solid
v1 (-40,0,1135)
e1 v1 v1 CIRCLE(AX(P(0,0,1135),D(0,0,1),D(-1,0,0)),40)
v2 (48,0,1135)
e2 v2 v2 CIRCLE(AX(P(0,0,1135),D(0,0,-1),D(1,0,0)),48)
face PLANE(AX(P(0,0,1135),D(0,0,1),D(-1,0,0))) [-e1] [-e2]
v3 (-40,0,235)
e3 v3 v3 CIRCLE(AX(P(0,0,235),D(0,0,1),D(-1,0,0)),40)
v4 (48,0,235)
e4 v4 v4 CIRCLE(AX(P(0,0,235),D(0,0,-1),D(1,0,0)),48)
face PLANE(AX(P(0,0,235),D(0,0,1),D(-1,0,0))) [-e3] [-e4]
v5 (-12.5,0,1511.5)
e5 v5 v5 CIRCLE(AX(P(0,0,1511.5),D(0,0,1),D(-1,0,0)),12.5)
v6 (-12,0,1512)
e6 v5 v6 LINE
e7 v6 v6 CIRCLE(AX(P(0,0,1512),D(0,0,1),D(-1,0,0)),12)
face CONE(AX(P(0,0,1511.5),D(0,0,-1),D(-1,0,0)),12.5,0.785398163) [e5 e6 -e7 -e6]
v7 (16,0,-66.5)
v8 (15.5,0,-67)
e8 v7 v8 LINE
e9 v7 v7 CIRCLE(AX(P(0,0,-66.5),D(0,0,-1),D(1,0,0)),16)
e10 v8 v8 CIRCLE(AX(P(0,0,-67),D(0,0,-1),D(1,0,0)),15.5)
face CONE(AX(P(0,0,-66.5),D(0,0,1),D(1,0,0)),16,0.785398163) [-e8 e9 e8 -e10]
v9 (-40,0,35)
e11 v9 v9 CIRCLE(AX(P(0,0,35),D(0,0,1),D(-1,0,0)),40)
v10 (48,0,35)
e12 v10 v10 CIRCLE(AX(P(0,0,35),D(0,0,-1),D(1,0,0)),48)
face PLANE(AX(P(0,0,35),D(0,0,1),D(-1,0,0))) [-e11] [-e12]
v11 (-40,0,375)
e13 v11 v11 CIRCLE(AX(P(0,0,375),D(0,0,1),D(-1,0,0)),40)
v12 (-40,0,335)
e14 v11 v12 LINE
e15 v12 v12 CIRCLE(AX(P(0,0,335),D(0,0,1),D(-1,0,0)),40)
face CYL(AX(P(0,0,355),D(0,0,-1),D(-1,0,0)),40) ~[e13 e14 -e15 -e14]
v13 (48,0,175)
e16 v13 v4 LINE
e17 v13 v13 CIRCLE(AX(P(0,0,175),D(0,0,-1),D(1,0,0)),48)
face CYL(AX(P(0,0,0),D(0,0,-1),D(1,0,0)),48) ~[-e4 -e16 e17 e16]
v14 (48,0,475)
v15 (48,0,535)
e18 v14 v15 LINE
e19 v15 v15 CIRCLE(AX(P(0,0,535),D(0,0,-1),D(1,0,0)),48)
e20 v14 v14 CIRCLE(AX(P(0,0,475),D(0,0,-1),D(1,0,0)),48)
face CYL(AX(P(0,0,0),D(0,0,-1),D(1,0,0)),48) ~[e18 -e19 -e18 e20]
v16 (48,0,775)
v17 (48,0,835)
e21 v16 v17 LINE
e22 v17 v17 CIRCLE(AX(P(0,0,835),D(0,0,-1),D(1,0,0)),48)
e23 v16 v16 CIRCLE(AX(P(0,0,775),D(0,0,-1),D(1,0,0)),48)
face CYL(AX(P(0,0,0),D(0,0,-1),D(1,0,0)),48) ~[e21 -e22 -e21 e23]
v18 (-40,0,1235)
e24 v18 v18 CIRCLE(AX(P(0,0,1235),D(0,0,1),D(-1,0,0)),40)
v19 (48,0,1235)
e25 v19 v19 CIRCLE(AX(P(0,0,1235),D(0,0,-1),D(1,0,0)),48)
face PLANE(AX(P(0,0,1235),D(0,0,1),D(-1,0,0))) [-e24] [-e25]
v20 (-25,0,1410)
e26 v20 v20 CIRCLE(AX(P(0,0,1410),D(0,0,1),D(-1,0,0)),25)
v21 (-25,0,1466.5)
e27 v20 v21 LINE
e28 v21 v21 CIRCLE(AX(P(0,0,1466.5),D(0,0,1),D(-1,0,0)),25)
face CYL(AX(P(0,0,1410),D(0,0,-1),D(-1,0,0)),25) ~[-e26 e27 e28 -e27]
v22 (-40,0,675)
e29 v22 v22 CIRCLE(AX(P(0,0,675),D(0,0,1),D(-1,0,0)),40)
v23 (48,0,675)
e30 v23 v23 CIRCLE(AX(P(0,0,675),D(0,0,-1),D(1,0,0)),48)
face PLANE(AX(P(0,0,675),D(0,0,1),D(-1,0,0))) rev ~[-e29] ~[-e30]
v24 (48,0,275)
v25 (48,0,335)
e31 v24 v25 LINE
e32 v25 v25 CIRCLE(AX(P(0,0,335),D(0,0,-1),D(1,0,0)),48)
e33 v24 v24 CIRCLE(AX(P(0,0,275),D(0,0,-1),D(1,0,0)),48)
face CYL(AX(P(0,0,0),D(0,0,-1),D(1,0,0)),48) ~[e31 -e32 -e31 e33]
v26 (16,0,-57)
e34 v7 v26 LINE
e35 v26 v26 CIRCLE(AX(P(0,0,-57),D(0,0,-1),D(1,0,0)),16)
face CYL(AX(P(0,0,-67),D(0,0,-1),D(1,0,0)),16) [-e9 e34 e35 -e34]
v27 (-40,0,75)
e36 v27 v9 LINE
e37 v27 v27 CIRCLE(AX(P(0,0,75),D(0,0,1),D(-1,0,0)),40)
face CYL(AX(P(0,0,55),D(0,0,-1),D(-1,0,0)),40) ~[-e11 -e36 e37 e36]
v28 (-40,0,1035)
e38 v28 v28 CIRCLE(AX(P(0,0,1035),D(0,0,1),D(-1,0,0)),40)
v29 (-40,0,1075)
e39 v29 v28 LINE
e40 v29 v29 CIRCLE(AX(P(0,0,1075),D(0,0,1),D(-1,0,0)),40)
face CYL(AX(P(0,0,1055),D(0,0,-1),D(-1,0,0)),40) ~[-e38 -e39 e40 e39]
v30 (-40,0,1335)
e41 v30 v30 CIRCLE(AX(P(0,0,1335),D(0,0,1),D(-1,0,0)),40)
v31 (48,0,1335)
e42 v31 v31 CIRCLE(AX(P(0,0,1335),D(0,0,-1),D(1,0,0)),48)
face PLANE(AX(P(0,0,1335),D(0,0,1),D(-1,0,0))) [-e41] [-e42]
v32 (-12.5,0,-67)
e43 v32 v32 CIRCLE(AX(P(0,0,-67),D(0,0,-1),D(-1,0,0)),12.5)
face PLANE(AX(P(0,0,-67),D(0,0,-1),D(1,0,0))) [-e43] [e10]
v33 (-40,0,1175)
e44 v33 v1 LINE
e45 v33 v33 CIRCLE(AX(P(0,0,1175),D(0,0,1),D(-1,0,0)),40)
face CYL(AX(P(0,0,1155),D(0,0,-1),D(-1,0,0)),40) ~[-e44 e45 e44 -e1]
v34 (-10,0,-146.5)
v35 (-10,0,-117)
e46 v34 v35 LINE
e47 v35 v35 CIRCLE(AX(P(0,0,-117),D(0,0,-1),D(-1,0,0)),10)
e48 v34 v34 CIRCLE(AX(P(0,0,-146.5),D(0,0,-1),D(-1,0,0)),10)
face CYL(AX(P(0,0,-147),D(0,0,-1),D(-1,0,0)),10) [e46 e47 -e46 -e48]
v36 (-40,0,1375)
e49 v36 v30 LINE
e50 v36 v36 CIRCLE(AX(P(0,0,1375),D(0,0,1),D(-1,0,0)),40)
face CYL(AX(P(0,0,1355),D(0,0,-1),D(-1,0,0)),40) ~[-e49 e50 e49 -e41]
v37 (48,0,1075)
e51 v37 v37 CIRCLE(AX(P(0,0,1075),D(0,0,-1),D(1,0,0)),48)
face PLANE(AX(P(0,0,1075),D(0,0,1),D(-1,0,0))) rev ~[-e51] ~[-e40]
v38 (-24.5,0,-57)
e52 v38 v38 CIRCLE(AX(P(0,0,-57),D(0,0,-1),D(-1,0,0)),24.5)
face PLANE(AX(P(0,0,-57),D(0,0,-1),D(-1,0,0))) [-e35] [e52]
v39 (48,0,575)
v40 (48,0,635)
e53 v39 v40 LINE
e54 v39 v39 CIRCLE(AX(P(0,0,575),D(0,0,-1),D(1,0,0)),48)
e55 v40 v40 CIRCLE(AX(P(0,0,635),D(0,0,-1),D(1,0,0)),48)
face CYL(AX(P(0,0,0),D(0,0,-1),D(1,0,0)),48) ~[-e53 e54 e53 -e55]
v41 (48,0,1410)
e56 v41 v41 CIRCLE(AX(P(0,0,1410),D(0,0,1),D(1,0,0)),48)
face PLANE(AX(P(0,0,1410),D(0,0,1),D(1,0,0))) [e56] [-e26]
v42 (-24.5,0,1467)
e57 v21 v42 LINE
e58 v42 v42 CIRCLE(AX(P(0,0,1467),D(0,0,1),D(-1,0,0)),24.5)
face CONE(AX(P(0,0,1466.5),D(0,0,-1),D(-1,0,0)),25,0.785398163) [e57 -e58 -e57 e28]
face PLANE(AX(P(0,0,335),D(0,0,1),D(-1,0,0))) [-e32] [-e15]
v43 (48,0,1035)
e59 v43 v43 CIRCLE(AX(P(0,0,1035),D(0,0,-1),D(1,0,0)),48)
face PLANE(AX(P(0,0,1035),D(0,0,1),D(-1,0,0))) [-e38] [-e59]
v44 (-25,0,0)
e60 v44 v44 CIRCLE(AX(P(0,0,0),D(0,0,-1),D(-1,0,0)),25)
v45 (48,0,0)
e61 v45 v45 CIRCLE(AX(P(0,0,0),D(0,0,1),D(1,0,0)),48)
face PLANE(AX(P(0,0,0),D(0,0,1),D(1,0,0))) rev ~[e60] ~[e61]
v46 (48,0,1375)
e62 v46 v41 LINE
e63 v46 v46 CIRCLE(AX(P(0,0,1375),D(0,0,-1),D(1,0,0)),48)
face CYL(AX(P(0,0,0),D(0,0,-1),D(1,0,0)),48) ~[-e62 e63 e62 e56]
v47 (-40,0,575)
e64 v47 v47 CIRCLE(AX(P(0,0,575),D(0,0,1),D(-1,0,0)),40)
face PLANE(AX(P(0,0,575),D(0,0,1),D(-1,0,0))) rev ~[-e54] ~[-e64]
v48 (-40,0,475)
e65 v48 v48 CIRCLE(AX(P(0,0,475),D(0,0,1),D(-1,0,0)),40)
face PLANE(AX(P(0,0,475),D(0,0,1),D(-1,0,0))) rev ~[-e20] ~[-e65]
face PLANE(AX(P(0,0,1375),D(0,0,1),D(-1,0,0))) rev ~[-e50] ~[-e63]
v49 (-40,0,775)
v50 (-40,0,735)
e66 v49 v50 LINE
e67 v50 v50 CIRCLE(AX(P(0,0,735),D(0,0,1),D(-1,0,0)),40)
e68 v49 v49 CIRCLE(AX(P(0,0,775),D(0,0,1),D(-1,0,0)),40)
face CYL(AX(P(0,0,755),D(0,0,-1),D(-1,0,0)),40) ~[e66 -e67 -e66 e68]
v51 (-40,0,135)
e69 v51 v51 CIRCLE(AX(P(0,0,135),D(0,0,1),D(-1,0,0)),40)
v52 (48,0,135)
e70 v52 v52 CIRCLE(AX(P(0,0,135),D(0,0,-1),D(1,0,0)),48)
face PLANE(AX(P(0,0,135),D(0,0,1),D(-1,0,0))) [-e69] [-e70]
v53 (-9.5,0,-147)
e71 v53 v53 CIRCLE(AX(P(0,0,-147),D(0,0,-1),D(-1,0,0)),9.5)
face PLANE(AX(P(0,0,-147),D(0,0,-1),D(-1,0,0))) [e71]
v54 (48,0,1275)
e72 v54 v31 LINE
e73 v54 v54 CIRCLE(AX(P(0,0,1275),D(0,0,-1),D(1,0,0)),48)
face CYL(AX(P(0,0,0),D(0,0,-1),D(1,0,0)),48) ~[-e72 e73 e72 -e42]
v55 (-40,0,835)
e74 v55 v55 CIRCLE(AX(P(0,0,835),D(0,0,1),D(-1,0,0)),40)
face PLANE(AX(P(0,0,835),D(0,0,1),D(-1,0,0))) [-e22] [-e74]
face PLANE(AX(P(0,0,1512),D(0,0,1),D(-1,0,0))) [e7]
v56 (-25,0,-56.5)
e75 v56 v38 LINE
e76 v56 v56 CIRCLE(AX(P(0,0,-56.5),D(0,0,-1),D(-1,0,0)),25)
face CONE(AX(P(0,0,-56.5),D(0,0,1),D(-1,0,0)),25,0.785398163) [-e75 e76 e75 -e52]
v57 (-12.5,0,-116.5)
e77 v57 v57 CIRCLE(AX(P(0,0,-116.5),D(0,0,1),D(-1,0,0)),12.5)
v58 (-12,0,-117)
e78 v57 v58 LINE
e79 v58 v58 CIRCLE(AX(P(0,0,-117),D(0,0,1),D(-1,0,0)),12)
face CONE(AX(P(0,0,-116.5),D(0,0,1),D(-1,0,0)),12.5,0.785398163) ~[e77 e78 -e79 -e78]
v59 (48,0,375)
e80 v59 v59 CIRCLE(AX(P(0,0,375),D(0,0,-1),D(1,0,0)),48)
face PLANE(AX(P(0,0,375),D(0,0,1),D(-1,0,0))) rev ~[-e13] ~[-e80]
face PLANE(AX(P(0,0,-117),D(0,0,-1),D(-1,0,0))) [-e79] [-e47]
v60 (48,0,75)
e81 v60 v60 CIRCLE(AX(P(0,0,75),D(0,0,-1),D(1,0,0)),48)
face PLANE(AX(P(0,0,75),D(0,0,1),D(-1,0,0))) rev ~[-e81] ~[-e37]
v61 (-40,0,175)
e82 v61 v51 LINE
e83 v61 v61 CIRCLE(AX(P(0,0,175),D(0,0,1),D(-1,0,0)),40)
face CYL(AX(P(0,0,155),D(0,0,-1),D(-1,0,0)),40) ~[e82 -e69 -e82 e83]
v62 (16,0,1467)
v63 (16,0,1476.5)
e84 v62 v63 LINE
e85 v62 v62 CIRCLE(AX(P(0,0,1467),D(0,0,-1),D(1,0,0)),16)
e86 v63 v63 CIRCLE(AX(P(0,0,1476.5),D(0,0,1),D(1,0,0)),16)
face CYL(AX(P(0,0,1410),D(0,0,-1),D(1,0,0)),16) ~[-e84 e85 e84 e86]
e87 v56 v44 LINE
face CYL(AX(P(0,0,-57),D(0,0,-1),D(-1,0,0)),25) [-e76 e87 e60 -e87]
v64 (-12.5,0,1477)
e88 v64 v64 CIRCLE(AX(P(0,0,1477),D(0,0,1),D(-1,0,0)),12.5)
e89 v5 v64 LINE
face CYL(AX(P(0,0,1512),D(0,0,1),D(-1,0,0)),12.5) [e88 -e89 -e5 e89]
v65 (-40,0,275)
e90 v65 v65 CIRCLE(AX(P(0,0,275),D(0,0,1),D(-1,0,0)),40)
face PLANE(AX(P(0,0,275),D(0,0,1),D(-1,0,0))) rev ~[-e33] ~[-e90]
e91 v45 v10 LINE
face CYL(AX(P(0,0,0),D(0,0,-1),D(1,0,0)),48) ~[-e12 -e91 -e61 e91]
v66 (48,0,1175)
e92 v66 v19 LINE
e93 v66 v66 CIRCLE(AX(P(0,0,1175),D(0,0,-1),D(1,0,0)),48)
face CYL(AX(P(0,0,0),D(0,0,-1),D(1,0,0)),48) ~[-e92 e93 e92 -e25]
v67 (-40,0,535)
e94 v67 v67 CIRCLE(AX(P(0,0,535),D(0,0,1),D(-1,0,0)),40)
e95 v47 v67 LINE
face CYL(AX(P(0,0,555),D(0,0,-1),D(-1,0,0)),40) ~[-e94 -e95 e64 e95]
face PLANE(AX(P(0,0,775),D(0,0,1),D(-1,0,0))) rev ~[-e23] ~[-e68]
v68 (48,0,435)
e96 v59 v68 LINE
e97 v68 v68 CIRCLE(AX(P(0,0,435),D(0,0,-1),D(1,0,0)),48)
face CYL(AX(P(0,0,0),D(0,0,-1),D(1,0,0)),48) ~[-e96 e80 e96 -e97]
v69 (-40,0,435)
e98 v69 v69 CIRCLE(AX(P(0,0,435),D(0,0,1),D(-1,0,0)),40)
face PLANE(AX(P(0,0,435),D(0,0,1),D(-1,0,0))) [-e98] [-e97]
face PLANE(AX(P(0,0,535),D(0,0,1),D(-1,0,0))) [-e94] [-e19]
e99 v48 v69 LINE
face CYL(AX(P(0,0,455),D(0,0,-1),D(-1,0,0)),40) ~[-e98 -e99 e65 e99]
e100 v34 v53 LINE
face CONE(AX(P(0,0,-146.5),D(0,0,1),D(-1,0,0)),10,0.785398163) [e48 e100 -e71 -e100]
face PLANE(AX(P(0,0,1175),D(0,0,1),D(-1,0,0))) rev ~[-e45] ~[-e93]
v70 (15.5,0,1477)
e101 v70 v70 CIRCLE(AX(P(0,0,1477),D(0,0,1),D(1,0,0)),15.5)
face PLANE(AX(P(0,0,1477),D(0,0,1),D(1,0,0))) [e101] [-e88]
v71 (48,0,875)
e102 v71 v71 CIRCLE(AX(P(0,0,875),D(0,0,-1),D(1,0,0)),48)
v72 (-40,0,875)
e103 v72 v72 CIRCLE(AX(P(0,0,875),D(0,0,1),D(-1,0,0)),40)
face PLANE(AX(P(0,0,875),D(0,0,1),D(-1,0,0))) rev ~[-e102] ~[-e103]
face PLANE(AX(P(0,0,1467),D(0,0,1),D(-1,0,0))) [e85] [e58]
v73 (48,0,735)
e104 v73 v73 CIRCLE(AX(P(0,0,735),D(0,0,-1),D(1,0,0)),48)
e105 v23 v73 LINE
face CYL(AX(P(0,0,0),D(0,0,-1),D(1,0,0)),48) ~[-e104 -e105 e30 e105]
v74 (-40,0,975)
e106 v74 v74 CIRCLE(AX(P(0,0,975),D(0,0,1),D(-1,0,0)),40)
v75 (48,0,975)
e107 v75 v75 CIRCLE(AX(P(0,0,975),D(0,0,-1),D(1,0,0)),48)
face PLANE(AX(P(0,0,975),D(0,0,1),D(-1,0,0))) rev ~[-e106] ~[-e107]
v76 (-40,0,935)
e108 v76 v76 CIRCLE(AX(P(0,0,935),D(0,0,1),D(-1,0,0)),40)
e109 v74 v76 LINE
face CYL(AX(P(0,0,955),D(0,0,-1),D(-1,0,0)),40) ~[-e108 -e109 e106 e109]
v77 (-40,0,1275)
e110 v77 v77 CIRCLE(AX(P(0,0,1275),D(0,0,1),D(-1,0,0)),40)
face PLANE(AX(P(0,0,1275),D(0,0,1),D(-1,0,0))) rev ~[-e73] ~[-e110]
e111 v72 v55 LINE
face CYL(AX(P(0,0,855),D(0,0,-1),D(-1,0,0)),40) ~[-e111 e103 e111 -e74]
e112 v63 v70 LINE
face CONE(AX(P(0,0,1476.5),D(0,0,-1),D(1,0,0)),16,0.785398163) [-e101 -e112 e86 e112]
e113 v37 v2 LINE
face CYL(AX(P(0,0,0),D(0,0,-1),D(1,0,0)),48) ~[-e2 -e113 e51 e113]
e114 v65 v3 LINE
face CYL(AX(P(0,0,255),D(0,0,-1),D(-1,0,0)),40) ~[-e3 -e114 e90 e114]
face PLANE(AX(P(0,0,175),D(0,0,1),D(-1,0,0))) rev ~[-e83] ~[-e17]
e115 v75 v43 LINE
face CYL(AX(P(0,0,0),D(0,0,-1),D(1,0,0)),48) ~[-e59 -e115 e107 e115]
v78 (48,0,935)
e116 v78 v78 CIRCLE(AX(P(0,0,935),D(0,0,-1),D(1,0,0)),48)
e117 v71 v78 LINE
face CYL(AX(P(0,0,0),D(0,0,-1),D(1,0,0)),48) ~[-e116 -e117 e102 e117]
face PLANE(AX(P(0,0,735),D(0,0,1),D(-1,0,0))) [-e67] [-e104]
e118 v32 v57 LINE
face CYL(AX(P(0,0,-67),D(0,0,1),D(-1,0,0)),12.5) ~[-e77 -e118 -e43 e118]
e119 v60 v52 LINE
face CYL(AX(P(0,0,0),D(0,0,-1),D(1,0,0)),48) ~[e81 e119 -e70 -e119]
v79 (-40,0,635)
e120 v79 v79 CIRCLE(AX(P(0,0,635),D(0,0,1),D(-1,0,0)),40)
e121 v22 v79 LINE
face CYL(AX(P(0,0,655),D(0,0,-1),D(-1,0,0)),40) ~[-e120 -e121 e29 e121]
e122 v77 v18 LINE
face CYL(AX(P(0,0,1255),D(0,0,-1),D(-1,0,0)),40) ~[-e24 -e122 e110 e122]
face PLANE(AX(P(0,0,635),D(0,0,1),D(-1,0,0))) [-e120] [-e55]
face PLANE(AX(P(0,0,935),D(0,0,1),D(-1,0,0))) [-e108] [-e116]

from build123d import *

# Parameters (mm, degrees)
SKETCH_1_R             = 48
EXTRUDE_1_DEPTH        = 1410
SKETCH_2_R             = 16
EXTRUDE_2_DEPTH        = 67
EXTRUDE_START          = 67
SKETCH_3_R             = 16
EXTRUDE_3_DEPTH        = 67
SKETCH_4_R             = 12.5
EXTRUDE_4_DEPTH        = 80
EXTRUDE_START_2        = 35
SKETCH_5_R             = 12.5
EXTRUDE_5_DEPTH        = 35
SKETCH_6_OUTSIDE_W     = 430.91
SKETCH_6_OUTSIDE_H     = 430.91
SKETCH_6_OUTSIDE_R     = 10
CUT_EXTRUDE_1_DEPTH    = 30
SKETCH_7_W             = 40
SKETCH_7_H             = 8
PATTERN_LINEAR_1_COUNT = 14
PATTERN_LINEAR_1_PITCH = 100
SKETCH_9_R             = 25
EXTRUDE_6_DEPTH        = 57
EXTRUDE_START_3        = 57
SKETCH_10_R            = 25
EXTRUDE_7_DEPTH        = 57
CHAMFER_1_SIZE         = 0.5


with BuildPart() as part:
    # 草图1 → 凸台-拉伸1 (new body)
    with BuildSketch(Plane.XY):
        Circle(SKETCH_1_R)
    extrude(amount=EXTRUDE_1_DEPTH)

    # 草图2 → 凸台-拉伸2 (add)
    with BuildSketch(Plane.XY.offset(1410)):
        Circle(SKETCH_2_R)
    extrude(amount=EXTRUDE_2_DEPTH)

    # 草图3 → 凸台-拉伸3 (add)
    with BuildSketch(Plane(origin=(0, 0, 0), x_dir=(-1, 0, 0), z_dir=(0, 0, -1)).offset(EXTRUDE_START)):
        with Locations(Location((0, 0, 0), (0, 0, 180))):
            Circle(SKETCH_3_R)
    extrude(amount=-EXTRUDE_3_DEPTH)

    # 草图4 → 凸台-拉伸4 (add)
    with BuildSketch(Plane(origin=(0, 0, -67), x_dir=(-1, 0, 0), z_dir=(0, 0, -1))):
        Circle(SKETCH_4_R)
    extrude(amount=EXTRUDE_4_DEPTH)

    # 草图5 → 凸台-拉伸5 (add)
    with BuildSketch(Plane.XY.offset(1477).offset(EXTRUDE_START_2)):
        with Locations(Location((0, 0, 0), (0, 0, 180))):
            Circle(SKETCH_5_R)
    extrude(amount=-EXTRUDE_5_DEPTH)

    # 草图6 outside → 切除-拉伸1 (cut)
    with BuildSketch(Plane(origin=(0, 0, -147), x_dir=(-1, 0, 0), z_dir=(0, 0, -1))):
        Rectangle(SKETCH_6_OUTSIDE_W, SKETCH_6_OUTSIDE_H)
        Circle(SKETCH_6_OUTSIDE_R, mode=Mode.SUBTRACT)
    extrude(amount=-CUT_EXTRUDE_1_DEPTH, mode=Mode.SUBTRACT)

    # 草图7 → 切除-旋转1 (revolve, cut)
    with BuildSketch(Plane(origin=(0, 0, 0), x_dir=(0, 0, -1), z_dir=(1, 0, 0)), mode=Mode.PRIVATE) as cut_revolve_1_sk:
        with Locations((-55, -44)):
            Rectangle(SKETCH_7_W, SKETCH_7_H)
    cut_revolve_1 = revolve(cut_revolve_1_sk.sketch.rotate(Axis((0, 0, 0), (0, 0, 1)), 270), axis=Axis((0, 0, 0), (0, 0, 1)), mode=Mode.SUBTRACT)

    # 阵列(线性)1: 切除-旋转1 ×14
    with Locations(*[(0, 0, i * PATTERN_LINEAR_1_PITCH) for i in range(1, PATTERN_LINEAR_1_COUNT)]):
        add(cut_revolve_1, mode=Mode.SUBTRACT)

    # 草图9 → 凸台-拉伸6 (add)
    with BuildSketch(Plane.XY.offset(1410)):
        with Locations(Location((0, 0, 0), (0, 0, 180))):
            Circle(SKETCH_9_R)
    extrude(amount=EXTRUDE_6_DEPTH)

    # 草图10 → 凸台-拉伸7 (add)
    with BuildSketch(Plane(origin=(0, 0, 0), x_dir=(-1, 0, 0), z_dir=(0, 0, -1)).offset(EXTRUDE_START_3)):
        Circle(SKETCH_10_R)
    extrude(amount=-EXTRUDE_7_DEPTH)

    # 倒角1
    chamfer_1_edges = [part.edges().sort_by_distance(p)[0] for p in [
        (-16, 0, -67),
        (25, 0, 1467),
        (25, 0, -57),
        (12.5, 0, 1512),
        (12.5, 0, -117),
        (10, 0, -147),
        (-16, 0, 1477),
    ]]
    chamfer(chamfer_1_edges, length=CHAMFER_1_SIZE)


solid = part.part
